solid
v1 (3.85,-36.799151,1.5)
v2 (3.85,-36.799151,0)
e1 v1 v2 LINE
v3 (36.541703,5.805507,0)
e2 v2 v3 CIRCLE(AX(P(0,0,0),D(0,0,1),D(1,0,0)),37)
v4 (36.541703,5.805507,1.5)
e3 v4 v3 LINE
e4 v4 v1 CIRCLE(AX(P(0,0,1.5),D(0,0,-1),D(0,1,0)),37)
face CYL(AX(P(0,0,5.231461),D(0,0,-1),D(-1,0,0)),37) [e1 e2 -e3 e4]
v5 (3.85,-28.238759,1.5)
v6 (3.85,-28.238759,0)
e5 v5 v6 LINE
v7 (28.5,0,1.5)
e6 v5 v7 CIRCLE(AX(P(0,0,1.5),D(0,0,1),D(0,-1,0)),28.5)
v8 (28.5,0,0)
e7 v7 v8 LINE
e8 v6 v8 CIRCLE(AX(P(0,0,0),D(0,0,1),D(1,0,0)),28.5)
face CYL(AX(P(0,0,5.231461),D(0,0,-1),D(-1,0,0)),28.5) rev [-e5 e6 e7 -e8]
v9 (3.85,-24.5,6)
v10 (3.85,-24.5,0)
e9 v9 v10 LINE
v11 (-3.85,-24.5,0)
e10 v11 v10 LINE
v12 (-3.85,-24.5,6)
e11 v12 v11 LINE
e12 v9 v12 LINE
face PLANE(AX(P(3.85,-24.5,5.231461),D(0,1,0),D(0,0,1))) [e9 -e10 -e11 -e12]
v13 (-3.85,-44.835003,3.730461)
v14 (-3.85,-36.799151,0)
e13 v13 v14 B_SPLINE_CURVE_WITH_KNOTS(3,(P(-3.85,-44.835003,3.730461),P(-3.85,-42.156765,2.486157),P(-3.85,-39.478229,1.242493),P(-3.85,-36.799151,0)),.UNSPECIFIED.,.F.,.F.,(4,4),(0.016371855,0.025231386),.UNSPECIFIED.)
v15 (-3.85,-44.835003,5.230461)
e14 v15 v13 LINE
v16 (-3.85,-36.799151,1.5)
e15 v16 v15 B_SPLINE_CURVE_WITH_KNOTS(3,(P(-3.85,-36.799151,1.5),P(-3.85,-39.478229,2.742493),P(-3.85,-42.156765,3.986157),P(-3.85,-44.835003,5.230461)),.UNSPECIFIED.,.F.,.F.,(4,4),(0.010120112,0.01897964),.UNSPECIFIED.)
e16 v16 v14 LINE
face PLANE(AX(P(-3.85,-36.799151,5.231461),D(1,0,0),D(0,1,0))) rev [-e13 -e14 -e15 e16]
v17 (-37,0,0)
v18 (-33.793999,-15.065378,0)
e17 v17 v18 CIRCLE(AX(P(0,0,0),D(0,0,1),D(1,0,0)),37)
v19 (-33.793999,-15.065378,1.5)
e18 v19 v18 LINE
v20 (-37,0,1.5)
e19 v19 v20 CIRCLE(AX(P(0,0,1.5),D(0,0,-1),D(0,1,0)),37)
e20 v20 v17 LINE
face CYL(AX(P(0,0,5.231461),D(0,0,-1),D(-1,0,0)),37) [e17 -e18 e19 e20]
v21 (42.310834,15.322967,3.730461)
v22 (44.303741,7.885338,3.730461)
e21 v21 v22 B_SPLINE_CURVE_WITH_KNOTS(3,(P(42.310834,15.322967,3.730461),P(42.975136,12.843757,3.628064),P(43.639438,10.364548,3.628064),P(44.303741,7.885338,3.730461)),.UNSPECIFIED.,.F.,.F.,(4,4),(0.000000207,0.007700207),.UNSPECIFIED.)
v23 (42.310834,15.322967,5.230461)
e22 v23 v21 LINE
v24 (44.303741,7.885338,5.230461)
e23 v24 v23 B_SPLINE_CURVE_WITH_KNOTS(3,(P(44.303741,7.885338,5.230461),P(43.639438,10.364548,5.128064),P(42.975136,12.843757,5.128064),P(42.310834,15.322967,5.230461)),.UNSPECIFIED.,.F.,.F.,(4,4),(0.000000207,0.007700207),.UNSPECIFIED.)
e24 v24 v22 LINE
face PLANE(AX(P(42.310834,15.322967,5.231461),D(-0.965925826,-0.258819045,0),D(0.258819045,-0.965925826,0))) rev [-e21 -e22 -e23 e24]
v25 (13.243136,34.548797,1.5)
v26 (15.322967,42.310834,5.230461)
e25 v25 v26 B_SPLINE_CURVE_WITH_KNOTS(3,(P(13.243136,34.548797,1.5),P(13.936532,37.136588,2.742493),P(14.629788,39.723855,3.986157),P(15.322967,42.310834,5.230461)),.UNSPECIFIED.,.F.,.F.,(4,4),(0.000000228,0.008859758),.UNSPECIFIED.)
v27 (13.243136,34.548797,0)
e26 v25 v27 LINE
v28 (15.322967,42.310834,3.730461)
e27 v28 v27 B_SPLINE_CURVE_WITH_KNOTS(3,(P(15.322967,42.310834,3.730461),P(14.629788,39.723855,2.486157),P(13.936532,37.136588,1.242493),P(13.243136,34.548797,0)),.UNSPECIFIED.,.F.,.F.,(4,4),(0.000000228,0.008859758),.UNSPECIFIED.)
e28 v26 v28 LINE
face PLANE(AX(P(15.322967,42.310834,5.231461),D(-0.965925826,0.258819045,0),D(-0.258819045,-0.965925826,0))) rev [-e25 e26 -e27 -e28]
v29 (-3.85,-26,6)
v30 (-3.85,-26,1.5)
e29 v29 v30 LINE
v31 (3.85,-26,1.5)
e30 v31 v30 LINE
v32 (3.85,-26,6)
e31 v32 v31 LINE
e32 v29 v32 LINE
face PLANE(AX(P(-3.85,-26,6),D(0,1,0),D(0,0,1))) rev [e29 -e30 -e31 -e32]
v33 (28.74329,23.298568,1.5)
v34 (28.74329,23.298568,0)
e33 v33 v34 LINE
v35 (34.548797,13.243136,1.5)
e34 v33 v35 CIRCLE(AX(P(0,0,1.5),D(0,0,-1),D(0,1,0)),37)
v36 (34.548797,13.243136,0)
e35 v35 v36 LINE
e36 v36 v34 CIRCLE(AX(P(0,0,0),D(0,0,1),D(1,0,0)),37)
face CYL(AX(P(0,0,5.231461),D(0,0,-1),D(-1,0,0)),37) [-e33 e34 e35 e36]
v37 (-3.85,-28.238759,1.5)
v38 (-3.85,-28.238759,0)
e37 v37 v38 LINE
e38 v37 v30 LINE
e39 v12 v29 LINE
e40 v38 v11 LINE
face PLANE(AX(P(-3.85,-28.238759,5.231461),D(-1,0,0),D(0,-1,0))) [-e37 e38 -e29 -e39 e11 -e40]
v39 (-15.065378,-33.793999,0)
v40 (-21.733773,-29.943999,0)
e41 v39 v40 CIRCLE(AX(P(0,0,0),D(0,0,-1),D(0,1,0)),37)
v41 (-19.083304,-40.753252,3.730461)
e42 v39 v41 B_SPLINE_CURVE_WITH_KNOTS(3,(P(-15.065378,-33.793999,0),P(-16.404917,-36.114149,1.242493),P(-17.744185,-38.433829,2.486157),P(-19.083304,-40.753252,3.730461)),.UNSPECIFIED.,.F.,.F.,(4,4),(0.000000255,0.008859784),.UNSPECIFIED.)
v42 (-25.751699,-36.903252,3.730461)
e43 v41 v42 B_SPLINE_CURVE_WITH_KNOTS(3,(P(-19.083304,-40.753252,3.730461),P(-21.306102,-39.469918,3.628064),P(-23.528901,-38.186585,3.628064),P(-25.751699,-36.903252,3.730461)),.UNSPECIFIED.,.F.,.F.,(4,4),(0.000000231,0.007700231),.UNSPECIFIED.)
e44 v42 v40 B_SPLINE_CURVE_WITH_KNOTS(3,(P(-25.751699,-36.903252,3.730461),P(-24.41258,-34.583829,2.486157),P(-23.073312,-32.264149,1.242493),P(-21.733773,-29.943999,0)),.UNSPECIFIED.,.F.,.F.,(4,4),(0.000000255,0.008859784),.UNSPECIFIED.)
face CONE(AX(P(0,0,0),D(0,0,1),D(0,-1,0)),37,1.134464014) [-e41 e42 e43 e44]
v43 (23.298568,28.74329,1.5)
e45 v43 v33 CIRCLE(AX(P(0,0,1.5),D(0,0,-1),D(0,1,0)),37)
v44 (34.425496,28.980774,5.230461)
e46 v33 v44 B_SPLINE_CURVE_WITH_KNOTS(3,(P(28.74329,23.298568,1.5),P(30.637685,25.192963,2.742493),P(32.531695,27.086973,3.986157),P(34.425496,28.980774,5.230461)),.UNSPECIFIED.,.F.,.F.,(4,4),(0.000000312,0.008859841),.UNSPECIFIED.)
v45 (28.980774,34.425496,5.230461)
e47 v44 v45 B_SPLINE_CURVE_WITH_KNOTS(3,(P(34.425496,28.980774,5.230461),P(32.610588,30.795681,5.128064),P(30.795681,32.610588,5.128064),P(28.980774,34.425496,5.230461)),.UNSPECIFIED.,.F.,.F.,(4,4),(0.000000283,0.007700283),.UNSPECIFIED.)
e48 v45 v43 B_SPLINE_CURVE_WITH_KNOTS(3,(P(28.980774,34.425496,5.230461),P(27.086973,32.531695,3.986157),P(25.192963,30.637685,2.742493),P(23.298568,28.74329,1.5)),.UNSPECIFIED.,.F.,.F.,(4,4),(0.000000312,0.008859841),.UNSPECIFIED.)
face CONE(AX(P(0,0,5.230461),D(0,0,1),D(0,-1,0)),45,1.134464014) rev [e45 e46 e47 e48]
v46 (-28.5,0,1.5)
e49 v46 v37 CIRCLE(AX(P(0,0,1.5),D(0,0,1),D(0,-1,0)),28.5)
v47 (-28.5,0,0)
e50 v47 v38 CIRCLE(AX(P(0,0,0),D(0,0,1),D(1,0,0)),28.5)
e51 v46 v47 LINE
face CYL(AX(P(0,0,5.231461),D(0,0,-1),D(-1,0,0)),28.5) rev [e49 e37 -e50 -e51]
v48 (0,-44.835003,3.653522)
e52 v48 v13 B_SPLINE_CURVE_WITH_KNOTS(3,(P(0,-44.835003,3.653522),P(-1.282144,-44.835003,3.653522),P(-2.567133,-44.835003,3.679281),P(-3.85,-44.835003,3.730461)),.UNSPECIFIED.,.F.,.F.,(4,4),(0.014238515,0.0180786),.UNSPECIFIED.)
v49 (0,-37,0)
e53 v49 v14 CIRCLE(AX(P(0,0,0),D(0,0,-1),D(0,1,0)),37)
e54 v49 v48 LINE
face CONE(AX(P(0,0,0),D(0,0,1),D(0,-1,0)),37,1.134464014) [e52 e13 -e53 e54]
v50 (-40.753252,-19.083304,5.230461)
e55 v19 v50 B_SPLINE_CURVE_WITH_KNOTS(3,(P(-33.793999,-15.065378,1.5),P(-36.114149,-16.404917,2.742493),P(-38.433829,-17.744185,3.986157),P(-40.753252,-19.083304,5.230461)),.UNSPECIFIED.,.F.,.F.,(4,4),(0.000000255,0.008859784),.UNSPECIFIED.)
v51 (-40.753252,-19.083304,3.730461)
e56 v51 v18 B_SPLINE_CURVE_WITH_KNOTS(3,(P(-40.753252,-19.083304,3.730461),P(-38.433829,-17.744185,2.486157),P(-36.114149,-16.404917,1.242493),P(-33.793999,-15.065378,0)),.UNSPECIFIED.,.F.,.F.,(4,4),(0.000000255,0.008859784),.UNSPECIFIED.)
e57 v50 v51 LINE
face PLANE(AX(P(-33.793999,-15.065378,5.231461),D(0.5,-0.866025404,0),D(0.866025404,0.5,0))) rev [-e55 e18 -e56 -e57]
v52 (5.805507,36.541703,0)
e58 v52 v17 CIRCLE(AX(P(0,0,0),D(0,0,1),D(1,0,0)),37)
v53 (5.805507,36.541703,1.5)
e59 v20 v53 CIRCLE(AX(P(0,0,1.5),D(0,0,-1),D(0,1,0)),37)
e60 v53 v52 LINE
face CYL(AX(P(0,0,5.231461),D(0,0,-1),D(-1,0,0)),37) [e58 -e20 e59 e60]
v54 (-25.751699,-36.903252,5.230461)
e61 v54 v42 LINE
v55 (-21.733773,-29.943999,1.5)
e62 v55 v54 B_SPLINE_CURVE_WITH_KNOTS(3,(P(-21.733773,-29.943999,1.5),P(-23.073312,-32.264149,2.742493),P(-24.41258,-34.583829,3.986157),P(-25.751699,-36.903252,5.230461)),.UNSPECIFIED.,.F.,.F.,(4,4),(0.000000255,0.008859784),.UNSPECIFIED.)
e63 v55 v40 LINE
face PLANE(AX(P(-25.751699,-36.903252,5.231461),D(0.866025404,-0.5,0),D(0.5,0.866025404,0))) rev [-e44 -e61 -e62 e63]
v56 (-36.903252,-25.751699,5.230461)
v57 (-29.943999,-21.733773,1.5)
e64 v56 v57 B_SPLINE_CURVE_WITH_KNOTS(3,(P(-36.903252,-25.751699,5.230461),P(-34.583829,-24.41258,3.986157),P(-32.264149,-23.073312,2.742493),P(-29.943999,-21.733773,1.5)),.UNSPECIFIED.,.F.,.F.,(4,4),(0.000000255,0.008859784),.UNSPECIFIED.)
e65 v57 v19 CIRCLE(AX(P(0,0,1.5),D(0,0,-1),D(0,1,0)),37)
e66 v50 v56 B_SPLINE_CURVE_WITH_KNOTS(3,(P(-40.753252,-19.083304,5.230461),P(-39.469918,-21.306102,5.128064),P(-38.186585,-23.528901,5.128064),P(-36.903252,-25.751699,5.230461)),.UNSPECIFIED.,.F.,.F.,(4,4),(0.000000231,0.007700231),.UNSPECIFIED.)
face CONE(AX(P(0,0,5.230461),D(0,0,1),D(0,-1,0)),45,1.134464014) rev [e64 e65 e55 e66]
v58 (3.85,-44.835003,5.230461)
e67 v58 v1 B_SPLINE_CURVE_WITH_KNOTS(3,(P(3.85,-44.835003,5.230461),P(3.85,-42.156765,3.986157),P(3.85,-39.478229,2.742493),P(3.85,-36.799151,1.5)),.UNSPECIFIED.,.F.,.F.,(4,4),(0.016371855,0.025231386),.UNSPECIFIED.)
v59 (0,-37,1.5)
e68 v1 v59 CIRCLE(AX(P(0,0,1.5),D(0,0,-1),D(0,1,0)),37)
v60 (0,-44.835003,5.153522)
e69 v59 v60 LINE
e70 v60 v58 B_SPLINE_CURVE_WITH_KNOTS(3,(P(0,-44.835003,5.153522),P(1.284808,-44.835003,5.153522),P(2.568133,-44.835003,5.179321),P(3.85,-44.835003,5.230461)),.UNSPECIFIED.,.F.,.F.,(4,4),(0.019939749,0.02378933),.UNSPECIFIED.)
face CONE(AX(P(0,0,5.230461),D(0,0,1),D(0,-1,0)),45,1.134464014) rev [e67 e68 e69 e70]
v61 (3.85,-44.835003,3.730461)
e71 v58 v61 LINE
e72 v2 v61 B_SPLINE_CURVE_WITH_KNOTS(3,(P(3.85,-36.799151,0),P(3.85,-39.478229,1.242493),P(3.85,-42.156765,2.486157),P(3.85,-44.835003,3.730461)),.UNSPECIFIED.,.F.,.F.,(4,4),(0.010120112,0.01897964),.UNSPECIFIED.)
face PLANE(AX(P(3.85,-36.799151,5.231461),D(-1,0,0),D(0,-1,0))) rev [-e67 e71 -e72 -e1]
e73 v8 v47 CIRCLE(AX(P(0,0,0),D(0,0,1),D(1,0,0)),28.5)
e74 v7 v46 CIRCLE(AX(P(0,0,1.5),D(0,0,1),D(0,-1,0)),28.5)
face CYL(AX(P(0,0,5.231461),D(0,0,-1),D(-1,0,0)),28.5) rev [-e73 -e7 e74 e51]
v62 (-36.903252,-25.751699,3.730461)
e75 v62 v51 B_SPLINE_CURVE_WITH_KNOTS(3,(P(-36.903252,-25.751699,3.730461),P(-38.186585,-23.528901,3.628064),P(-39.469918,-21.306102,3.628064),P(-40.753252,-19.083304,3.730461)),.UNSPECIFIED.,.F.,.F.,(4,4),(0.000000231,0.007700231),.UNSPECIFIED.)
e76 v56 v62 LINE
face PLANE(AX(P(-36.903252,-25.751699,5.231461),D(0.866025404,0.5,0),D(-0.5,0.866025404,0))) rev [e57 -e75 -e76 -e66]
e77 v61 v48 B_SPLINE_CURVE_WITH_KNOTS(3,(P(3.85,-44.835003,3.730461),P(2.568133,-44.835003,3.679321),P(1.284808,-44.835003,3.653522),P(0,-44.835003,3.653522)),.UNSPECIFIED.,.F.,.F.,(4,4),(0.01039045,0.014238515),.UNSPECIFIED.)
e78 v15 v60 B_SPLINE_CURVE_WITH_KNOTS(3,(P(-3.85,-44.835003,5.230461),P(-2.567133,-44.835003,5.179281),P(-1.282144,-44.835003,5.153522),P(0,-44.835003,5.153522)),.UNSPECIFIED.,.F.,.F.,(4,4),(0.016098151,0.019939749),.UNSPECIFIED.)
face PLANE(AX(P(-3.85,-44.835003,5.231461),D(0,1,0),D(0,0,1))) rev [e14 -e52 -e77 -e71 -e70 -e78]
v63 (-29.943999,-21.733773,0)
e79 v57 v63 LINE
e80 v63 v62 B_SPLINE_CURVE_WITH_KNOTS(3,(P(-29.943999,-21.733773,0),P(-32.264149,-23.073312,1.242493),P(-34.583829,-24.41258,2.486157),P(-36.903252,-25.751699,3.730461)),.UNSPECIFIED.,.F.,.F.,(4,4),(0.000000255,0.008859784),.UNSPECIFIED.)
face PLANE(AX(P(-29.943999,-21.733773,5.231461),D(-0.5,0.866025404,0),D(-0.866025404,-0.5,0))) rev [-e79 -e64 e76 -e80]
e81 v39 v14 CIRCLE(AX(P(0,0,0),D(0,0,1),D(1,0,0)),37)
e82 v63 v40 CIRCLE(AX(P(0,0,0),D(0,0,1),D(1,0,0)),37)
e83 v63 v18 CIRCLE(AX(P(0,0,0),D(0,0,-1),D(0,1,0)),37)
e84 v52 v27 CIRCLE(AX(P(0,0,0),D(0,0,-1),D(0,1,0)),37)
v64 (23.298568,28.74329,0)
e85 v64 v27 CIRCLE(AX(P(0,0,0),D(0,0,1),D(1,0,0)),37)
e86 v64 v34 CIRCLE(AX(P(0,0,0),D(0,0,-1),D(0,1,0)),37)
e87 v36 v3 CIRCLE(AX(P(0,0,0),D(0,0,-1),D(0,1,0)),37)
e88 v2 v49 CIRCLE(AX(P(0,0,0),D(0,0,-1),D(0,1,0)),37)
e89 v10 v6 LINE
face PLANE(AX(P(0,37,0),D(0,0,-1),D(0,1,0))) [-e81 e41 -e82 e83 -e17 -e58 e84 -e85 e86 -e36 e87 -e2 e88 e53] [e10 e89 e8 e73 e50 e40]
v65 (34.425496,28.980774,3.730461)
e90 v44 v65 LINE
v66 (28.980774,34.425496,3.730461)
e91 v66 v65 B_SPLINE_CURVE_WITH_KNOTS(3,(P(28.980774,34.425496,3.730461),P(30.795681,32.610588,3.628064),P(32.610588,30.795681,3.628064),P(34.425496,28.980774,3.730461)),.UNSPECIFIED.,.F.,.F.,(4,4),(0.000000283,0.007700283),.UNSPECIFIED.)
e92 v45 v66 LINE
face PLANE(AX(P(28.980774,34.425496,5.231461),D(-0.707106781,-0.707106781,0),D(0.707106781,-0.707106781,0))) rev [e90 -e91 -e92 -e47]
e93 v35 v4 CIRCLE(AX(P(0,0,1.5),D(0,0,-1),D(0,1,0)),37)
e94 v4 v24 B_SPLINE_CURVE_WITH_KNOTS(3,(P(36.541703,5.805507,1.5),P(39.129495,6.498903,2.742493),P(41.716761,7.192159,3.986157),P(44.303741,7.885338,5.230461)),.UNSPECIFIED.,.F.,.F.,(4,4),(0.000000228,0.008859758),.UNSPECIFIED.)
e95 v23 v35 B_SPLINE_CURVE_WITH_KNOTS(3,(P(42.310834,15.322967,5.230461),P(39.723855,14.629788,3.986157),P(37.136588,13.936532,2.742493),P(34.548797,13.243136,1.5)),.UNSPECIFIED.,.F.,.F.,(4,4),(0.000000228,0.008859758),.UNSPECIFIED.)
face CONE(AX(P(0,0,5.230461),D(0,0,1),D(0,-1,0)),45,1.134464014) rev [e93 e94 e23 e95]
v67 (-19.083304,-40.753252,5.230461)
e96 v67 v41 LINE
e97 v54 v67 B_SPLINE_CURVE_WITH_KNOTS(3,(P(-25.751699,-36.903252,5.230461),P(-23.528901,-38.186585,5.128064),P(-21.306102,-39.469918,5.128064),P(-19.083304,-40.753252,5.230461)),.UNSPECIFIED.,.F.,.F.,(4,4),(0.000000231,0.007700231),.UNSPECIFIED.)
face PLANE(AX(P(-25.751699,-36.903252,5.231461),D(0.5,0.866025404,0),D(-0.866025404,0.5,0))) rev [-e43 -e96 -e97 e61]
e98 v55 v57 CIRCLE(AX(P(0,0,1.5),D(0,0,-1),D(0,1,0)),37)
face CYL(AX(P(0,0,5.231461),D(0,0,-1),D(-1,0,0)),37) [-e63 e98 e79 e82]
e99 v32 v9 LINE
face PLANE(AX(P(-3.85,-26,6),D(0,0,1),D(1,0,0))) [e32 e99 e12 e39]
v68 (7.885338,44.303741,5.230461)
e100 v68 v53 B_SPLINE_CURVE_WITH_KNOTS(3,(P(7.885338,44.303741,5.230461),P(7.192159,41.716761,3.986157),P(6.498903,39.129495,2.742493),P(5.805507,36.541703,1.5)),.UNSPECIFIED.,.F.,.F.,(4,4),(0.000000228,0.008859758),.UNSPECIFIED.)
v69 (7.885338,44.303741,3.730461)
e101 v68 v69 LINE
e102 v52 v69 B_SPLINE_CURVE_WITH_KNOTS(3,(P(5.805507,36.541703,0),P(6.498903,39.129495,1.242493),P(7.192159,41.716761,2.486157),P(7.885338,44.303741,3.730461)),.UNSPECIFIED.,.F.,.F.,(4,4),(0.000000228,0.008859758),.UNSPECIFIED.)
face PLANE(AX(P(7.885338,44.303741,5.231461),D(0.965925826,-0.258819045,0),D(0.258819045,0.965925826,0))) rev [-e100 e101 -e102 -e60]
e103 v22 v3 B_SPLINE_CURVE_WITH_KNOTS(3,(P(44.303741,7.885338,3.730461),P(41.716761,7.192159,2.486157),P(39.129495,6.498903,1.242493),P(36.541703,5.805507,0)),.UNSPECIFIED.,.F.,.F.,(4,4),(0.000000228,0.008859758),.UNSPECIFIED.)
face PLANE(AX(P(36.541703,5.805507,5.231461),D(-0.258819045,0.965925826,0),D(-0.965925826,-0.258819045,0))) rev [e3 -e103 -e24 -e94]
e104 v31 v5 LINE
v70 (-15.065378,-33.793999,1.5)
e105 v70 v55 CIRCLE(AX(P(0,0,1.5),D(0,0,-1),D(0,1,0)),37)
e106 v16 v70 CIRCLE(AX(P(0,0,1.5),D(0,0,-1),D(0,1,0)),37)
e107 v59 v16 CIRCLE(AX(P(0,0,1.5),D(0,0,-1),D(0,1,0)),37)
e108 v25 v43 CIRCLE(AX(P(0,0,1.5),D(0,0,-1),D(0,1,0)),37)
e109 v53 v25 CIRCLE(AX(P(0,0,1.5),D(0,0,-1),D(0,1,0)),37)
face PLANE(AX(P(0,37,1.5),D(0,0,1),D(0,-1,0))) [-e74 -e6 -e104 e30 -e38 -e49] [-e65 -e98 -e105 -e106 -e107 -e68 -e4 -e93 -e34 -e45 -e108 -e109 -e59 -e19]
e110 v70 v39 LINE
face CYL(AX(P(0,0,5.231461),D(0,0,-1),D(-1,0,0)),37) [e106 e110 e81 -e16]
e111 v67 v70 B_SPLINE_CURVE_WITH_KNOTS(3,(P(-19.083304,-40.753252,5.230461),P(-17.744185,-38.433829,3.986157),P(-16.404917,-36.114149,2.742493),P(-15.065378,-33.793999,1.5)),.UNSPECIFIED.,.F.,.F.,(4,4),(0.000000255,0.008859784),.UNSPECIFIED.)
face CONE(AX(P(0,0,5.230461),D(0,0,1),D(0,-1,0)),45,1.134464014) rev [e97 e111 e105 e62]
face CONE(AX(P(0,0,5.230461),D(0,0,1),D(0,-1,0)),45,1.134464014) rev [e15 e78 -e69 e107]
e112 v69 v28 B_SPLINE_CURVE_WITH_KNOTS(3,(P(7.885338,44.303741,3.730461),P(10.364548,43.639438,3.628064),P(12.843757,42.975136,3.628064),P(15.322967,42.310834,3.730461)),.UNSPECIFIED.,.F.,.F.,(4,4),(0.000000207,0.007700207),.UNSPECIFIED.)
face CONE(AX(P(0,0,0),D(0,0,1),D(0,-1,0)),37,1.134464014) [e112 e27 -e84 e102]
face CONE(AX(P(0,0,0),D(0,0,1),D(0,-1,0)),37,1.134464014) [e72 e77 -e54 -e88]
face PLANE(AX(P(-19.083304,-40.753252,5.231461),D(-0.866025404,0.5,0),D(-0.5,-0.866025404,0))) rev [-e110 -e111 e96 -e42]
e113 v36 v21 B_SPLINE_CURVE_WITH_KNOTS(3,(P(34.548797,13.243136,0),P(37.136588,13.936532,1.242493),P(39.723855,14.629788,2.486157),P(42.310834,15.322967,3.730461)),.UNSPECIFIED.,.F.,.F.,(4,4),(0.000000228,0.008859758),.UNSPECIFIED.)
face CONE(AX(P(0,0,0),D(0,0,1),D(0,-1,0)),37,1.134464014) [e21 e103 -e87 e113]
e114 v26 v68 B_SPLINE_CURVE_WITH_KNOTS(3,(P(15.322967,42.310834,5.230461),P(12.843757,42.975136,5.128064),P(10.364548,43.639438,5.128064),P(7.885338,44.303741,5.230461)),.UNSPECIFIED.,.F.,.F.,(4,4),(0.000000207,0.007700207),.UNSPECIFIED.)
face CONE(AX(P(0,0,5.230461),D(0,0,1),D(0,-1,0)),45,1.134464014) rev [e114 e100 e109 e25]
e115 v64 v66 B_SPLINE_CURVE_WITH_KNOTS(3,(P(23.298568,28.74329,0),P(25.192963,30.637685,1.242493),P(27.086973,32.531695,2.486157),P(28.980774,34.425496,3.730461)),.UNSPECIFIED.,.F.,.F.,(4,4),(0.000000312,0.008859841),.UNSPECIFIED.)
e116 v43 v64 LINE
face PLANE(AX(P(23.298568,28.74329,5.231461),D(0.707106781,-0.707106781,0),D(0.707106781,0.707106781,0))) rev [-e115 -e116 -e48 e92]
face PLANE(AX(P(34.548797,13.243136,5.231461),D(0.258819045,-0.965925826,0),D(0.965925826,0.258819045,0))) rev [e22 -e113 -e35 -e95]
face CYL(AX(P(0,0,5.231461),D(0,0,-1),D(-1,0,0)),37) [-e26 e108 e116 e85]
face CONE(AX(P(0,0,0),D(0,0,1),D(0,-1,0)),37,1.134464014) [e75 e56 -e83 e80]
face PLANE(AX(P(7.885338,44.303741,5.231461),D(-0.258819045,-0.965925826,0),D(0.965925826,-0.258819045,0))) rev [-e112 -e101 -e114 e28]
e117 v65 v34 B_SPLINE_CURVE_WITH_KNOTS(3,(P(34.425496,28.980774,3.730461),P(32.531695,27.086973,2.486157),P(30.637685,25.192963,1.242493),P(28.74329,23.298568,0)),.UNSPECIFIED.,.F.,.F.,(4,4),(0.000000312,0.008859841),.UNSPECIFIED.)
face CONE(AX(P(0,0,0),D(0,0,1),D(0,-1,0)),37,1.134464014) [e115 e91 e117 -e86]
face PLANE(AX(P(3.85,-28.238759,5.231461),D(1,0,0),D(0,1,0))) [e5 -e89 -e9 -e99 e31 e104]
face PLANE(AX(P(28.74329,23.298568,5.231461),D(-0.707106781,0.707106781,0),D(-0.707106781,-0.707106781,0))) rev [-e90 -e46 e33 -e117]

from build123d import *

# Parameters (mm, degrees)
SKETCH3_OUTSIDE_W   = 117.478
SKETCH3_OUTSIDE_H   = 117.478
CUT_EXTRUDE2_DEPTH  = 5.230463
SKETCH4_W           = 7.7
SKETCH4_H           = 1.5
BOSS_EXTRUDE1_DEPTH = 6


with BuildPart() as part:
    # Sketch2 → Boss-Revolve (revolve)
    with BuildSketch(Plane(origin=(0, 0, 0), x_dir=(0, 0, -1), z_dir=(1, 0, 0))):
        Polygon((-3.730461265, 45), (0, 37), (0, 0), (-1.5, 0), (-1.5, 37), (-5.230461265, 45), align=None)
    revolve(axis=Axis((0, 0, 0), (0, 0, 1)))

    # Sketch3 outside → Cut-Extrude2 (cut)
    # profile 1 of 2: a face of its own
    with BuildSketch(Plane.XY):
        Rectangle(SKETCH3_OUTSIDE_W, SKETCH3_OUTSIDE_H)
        with BuildLine():
            Line((-3.85, -36.799150805), (-3.85, -44.835003067))
            Line((-3.85, -44.835003067), (3.85, -44.835003067))
            Line((3.85, -44.835003067), (3.85, -36.799150805))
            ThreePointArc((3.85, -36.799150805), (29.354073591, -22.524172873), (36.541703472, 5.805506641))
            Line((36.541703472, 5.805506641), (44.303740708, 7.88533825))
            Line((44.303740708, 7.88533825), (42.31083406, 15.322967112))
            Line((42.31083406, 15.322967112), (34.548796825, 13.243135503))
            ThreePointArc((34.548796825, 13.243135503), (32.04293994, 18.5), (28.743290184, 23.298567969))
            Line((28.743290184, 23.298567969), (34.425495811, 28.980773595))
            Line((34.425495811, 28.980773595), (28.980773595, 34.425495811))
            Line((28.980773595, 34.425495811), (23.298567969, 28.743290184))
            ThreePointArc((23.298567969, 28.743290184), (18.5, 32.04293994), (13.243135503, 34.548796825))
            Line((13.243135503, 34.548796825), (15.322967112, 42.31083406))
            Line((15.322967112, 42.31083406), (7.88533825, 44.303740708))
            Line((7.88533825, 44.303740708), (5.805506641, 36.541703472))
            ThreePointArc((5.805506641, 36.541703472), (-29.354073591, 22.524172873), (-33.793999435, -15.065377598))
            Line((-33.793999435, -15.065377598), (-40.753251635, -19.083303729))
            Line((-40.753251635, -19.083303729), (-36.903251635, -25.751699338))
            Line((-36.903251635, -25.751699338), (-29.943999435, -21.733773207))
            ThreePointArc((-29.943999435, -21.733773207), (-26.162950904, -26.162950904), (-21.733773207, -29.943999435))
            Line((-21.733773207, -29.943999435), (-25.751699338, -36.903251635))
            Line((-25.751699338, -36.903251635), (-19.083303729, -40.753251635))
            Line((-19.083303729, -40.753251635), (-15.065377598, -33.793999435))
            ThreePointArc((-15.065377598, -33.793999435), (-9.576304669, -35.739255573), (-3.85, -36.799150805))
        make_face(mode=Mode.SUBTRACT)
    # profile 2 of 2: a face of its own
    with BuildSketch(Plane.XY):
        with BuildLine():
            Line((3.85, -28.238758825), (3.85, -24.5))
            Line((3.85, -24.5), (-3.85, -24.5))
            Line((-3.85, -24.5), (-3.85, -28.238758825))
            ThreePointArc((-3.85, -28.238758825), (0, 28.5), (3.85, -28.238758825))
        make_face()
    extrude(amount=CUT_EXTRUDE2_DEPTH, mode=Mode.SUBTRACT)

    # Sketch4 → Boss-Extrude1 (add)
    with BuildSketch(Plane.XY):
        with Locations((0, -25.25)):
            Rectangle(SKETCH4_W, SKETCH4_H)
    extrude(amount=BOSS_EXTRUDE1_DEPTH)


solid = part.part
